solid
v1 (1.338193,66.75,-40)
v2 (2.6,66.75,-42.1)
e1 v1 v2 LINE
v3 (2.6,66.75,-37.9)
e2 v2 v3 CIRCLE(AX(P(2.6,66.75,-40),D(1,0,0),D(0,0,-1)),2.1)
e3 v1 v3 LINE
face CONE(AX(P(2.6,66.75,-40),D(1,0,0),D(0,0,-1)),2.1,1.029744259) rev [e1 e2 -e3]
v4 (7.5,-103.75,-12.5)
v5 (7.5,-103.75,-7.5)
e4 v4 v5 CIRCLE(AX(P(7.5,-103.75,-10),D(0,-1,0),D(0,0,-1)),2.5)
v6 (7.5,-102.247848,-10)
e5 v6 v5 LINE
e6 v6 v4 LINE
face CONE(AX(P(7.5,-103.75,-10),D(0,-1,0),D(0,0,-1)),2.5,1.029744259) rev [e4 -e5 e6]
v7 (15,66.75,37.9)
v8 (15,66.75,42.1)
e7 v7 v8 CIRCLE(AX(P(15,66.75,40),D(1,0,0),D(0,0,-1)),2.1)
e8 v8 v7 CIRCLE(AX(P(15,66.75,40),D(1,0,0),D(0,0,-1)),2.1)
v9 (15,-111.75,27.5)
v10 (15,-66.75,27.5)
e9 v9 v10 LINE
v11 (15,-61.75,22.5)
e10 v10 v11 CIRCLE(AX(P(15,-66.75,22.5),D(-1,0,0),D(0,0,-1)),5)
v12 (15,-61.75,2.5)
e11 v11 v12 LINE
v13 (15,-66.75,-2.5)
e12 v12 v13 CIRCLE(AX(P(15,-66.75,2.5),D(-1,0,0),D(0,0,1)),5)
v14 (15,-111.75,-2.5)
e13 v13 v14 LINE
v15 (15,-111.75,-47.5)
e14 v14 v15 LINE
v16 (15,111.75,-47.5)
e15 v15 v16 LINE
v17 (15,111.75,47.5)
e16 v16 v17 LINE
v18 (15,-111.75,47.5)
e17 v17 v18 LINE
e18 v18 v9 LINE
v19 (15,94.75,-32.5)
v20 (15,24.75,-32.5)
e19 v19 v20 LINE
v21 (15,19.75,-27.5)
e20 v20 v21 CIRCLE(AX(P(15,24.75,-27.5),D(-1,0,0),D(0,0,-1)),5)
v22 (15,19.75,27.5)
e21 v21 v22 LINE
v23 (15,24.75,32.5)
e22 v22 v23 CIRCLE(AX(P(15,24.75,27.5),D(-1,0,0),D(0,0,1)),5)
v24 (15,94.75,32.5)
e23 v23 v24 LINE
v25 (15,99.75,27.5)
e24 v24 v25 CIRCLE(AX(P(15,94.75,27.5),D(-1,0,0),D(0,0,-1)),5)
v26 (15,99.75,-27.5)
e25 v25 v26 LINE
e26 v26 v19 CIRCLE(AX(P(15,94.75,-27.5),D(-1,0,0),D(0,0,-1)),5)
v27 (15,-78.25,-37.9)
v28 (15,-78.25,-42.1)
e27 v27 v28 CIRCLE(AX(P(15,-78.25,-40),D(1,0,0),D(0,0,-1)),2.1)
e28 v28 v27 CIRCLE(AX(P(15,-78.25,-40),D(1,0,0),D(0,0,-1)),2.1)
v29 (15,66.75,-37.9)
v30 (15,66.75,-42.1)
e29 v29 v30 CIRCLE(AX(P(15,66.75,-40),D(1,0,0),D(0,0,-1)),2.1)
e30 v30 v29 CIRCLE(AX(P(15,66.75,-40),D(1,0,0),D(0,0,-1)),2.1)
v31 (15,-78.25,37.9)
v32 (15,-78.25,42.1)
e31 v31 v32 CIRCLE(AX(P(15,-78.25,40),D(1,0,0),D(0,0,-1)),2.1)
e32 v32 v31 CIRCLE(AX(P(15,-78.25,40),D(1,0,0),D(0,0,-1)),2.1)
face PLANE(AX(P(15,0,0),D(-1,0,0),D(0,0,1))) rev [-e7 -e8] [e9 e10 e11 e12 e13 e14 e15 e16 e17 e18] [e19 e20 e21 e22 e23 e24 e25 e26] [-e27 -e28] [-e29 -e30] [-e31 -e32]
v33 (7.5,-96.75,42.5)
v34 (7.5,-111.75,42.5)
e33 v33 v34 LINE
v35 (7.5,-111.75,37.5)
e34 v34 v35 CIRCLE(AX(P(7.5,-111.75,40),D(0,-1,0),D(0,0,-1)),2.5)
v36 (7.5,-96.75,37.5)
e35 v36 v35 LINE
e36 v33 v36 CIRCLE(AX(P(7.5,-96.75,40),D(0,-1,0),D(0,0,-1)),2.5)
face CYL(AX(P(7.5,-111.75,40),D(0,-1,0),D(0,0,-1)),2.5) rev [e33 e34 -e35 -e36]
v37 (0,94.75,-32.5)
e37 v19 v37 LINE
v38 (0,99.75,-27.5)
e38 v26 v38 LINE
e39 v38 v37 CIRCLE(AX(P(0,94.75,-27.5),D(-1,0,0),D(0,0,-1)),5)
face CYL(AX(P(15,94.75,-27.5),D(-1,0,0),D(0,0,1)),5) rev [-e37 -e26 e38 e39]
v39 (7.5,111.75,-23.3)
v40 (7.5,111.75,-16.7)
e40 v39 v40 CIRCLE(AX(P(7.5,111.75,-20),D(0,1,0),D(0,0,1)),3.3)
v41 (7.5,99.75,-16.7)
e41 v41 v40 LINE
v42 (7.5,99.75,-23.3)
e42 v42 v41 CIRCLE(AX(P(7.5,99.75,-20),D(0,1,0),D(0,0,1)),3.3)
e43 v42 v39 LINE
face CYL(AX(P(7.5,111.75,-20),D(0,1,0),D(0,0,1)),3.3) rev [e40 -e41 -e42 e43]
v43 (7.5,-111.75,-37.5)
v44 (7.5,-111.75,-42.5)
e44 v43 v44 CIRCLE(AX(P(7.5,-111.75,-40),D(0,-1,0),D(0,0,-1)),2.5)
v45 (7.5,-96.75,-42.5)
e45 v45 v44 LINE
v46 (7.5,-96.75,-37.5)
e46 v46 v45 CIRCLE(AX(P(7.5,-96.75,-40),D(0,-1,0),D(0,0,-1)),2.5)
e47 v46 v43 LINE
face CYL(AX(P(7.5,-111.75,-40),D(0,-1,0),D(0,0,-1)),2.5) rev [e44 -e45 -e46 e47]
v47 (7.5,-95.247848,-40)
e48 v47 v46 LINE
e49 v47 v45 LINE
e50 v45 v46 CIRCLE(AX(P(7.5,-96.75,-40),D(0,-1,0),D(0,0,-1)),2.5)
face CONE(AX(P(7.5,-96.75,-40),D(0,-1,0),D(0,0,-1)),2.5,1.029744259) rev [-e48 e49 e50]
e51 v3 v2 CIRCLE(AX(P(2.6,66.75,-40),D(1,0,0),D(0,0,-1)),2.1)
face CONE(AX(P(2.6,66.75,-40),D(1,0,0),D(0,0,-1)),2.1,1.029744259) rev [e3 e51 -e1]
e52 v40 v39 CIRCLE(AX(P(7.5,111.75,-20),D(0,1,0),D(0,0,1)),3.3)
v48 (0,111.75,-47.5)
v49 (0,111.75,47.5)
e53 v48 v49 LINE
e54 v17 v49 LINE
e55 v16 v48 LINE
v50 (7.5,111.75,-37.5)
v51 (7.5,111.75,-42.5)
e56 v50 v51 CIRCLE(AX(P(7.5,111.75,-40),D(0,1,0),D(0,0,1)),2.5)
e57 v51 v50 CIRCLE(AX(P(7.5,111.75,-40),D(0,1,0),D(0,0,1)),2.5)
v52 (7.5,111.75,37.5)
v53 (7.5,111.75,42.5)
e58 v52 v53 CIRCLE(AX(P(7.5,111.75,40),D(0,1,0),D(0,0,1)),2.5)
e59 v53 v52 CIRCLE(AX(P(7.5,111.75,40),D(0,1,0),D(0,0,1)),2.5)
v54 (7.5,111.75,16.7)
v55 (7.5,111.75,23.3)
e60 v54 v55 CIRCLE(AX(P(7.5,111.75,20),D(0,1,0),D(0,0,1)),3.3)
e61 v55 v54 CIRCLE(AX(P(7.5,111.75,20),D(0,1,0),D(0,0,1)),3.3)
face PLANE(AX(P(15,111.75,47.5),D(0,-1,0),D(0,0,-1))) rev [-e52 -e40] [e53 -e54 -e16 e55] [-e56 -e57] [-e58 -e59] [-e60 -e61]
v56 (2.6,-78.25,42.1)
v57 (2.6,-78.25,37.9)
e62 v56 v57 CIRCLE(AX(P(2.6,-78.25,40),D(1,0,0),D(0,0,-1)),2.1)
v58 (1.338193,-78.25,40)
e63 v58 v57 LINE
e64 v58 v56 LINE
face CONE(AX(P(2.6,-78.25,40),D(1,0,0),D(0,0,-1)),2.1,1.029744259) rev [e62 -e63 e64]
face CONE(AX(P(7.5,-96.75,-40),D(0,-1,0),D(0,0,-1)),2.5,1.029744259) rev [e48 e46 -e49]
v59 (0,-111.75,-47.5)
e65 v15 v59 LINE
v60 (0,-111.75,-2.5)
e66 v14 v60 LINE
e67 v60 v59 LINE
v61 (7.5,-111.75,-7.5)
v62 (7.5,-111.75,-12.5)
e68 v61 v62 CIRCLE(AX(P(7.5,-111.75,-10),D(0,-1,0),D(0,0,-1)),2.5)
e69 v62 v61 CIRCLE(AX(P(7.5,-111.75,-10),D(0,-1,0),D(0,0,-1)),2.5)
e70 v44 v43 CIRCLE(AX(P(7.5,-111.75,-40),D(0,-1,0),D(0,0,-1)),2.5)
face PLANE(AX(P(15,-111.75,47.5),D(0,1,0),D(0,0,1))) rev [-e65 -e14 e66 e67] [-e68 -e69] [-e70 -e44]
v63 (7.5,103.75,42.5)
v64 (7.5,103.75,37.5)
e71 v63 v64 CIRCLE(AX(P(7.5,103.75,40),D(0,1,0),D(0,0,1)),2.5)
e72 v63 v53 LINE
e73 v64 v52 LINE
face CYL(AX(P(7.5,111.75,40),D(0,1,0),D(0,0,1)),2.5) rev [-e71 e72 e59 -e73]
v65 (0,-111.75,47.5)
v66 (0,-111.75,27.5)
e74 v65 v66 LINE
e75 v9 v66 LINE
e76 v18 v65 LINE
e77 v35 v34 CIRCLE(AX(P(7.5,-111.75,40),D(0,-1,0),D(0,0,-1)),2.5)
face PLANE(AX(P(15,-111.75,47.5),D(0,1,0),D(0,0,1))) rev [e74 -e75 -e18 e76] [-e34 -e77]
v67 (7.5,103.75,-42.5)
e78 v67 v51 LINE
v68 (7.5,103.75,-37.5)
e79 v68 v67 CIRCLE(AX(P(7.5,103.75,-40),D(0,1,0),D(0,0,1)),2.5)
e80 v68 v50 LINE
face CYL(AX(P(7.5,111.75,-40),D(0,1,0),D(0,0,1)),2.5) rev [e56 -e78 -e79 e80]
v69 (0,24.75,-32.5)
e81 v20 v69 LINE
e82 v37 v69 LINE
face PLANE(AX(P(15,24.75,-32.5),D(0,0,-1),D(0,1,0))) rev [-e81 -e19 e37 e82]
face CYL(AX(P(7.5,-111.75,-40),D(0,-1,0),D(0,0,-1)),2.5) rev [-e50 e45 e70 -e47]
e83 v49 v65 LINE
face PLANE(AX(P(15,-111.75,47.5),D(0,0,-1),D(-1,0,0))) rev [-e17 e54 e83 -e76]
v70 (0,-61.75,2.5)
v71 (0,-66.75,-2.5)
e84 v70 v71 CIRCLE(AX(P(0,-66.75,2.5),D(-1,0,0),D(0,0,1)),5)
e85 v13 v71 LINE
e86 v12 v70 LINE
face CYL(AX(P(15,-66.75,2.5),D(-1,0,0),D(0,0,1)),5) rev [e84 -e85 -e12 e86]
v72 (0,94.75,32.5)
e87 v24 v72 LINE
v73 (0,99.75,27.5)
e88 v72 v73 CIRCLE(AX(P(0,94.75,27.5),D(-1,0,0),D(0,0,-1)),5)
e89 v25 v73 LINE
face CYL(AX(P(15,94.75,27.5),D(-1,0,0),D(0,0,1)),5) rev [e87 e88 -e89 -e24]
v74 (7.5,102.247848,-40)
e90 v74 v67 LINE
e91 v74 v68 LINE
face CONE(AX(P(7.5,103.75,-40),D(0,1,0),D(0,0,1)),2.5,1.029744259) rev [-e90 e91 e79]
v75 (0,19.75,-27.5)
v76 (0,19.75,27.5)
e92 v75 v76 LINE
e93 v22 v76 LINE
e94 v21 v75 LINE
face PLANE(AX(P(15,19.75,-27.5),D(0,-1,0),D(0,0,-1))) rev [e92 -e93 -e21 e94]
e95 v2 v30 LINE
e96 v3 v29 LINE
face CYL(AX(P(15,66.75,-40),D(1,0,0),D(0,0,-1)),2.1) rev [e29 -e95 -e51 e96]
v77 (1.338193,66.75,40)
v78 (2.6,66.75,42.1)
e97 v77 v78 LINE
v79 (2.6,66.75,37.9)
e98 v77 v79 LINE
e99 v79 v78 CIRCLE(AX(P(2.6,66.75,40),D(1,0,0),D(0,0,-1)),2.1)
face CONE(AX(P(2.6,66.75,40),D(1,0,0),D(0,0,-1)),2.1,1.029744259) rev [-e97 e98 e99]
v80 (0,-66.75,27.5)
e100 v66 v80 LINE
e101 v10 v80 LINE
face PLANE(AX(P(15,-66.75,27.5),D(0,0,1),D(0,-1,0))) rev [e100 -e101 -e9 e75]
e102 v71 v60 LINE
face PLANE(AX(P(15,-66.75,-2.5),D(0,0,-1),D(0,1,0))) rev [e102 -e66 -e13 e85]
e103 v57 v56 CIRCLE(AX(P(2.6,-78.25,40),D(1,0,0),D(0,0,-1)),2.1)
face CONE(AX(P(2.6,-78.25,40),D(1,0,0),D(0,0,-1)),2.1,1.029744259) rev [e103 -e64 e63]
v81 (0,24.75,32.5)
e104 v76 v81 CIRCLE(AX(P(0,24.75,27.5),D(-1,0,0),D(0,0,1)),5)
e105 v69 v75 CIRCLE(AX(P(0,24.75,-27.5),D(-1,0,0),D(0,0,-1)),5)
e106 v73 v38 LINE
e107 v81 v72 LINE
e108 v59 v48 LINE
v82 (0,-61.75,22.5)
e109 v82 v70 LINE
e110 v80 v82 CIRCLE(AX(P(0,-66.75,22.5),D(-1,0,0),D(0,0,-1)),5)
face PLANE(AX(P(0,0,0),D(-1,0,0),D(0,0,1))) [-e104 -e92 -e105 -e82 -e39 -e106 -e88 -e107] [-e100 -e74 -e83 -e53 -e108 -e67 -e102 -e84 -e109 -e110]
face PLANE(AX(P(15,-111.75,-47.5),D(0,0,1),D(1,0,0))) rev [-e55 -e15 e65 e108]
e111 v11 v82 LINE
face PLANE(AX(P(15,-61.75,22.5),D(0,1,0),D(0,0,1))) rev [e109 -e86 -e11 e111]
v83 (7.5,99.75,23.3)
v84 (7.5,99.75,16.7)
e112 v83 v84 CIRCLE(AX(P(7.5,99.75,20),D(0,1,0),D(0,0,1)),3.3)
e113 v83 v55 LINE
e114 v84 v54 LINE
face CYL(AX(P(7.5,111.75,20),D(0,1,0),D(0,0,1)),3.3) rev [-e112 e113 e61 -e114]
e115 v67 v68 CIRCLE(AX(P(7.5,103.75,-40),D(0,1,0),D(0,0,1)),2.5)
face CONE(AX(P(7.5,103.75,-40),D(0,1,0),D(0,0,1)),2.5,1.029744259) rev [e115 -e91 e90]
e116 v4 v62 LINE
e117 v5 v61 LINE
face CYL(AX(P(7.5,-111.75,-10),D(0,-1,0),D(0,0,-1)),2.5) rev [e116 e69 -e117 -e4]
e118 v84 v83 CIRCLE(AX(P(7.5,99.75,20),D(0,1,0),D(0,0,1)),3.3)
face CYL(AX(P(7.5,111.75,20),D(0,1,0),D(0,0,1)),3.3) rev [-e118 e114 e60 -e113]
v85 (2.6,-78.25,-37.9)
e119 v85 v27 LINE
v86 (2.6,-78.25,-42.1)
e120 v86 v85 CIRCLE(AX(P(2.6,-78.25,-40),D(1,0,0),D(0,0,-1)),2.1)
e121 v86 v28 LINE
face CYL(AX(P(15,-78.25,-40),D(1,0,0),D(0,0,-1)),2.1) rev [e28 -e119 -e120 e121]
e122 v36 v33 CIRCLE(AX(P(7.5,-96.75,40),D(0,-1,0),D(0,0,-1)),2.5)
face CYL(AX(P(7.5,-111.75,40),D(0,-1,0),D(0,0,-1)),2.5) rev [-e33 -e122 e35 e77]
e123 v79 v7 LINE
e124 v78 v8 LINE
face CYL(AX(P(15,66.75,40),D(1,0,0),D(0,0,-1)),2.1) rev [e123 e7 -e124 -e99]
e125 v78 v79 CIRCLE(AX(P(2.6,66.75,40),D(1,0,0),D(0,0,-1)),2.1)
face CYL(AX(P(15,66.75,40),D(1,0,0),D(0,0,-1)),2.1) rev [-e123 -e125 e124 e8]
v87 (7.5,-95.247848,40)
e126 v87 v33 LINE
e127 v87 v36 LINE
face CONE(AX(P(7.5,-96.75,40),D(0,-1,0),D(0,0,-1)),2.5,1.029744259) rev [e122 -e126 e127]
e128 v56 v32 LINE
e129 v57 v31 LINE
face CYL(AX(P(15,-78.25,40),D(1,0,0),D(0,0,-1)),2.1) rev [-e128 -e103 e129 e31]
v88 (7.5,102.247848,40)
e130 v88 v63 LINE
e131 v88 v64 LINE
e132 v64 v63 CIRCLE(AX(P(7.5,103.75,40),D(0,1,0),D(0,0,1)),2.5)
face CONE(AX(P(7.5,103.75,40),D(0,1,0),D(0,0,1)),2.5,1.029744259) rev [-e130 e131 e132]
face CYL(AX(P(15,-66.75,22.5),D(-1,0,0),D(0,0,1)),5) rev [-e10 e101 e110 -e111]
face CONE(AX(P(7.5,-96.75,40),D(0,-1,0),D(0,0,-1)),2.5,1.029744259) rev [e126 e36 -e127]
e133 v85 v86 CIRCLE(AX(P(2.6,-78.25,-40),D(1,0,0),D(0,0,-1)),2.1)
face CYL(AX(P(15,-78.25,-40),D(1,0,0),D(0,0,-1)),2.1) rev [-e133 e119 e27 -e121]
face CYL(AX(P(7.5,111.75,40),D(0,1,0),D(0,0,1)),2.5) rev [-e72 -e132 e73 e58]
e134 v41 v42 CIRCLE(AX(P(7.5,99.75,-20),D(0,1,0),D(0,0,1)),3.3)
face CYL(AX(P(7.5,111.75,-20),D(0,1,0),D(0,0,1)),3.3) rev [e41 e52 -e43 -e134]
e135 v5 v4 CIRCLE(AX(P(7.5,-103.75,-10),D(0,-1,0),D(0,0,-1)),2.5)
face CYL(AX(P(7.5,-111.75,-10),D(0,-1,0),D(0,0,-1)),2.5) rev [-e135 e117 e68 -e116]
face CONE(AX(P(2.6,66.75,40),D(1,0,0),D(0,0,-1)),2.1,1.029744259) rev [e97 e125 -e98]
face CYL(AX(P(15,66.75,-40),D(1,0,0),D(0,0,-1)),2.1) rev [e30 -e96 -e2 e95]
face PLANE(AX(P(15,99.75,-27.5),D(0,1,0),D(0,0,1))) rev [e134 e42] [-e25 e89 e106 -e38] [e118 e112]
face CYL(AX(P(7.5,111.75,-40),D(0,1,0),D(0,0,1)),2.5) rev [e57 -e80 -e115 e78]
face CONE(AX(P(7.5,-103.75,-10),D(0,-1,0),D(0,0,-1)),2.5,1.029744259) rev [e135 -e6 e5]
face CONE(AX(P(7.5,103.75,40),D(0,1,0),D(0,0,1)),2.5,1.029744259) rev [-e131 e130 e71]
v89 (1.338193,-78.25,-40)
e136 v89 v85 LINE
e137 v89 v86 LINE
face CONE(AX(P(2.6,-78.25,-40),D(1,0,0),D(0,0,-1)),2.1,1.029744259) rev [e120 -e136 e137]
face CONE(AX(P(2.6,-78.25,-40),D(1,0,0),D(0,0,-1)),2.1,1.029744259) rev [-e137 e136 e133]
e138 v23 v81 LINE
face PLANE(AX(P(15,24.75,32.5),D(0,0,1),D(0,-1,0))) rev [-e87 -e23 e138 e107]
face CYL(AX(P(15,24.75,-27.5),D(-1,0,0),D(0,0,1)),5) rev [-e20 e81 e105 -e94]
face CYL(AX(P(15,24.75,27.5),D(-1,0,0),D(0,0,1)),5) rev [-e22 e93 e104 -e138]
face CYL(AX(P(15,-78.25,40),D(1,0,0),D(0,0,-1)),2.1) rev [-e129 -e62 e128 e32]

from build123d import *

# Parameters (mm, degrees)
SKETCH1_W                  = 95
SKETCH1_H                  = 223.5
BOSS_EXTRUDE1_DEPTH        = 15
CUT_EXTRUDE1_DEPTH         = 123.349141803
M6_CLEARANCE_HOLE1_D       = 6.6
M6_CLEARANCE_HOLE1_DEPTH   = 19.75
M6_CLEARANCE_HOLE1_TIP     = 1.982840043
M6_TAPPED_HOLE1_D          = 5
M6_TAPPED_HOLE1_DEPTH      = 15
M6_TAPPED_HOLE1_TIP        = 1.502151548
F_5_0MM_BLIND_HOLE_1_D     = 5
F_5_0MM_BLIND_HOLE_1_DEPTH = 8
F_5_0MM_BLIND_HOLE_1_TIP   = 1.502151548
F_5_0MM_BLIND_HOLE_2_D     = 5
F_5_0MM_BLIND_HOLE_2_DEPTH = 8
F_5_0MM_BLIND_HOLE_2_TIP   = 1.502151548
M5_TAPPED_HOLE1_D          = 4.2
M5_TAPPED_HOLE1_DEPTH      = 12.4
M5_TAPPED_HOLE1_TIP        = 1.2618073


with BuildPart() as part:
    # Sketch1 → Boss-Extrude1 (new body)
    with BuildSketch(Plane(origin=(0, 0, 0), x_dir=(0, 0, -1), z_dir=(1, 0, 0))):
        Rectangle(SKETCH1_W, SKETCH1_H)
    extrude(amount=BOSS_EXTRUDE1_DEPTH)

    # Sketch2 → Cut-Extrude1 (cut, through all)
    with BuildSketch(Plane.ZY):
        with BuildLine():
            Line((22.5, -61.75), (2.5, -61.75))
            ThreePointArc((2.5, -61.75), (-1.035533906, -63.214466094), (-2.5, -66.75))
            Line((-2.5, -66.75), (-2.5, -111.75))
            Line((-2.5, -111.75), (27.5, -111.75))
            Line((27.5, -111.75), (27.5, -66.75))
            ThreePointArc((27.5, -66.75), (26.035533906, -63.214466094), (22.5, -61.75))
        make_face()
        with BuildLine():
            Line((-27.5, 19.75), (27.5, 19.75))
            ThreePointArc((27.5, 19.75), (31.035533906, 21.214466094), (32.5, 24.75))
            Line((32.5, 24.75), (32.5, 94.75))
            ThreePointArc((32.5, 94.75), (31.035533906, 98.285533906), (27.5, 99.75))
            Line((27.5, 99.75), (-27.5, 99.75))
            ThreePointArc((-27.5, 99.75), (-31.035533906, 98.285533906), (-32.5, 94.75))
            Line((-32.5, 94.75), (-32.5, 24.75))
            ThreePointArc((-32.5, 24.75), (-31.035533906, 21.214466094), (-27.5, 19.75))
        make_face()
    extrude(amount=-CUT_EXTRUDE1_DEPTH, mode=Mode.SUBTRACT)

    # M6 Clearance Hole1
    with Locations(Plane(origin=(0, 111.75, 0), x_dir=(1, 0, 0), z_dir=(0, 1, 0))):
        with Locations((7.5, -20), (7.5, 20)):
            Hole(M6_CLEARANCE_HOLE1_D / 2, depth=M6_CLEARANCE_HOLE1_DEPTH)
            with Locations((0, 0, -(M6_CLEARANCE_HOLE1_DEPTH + M6_CLEARANCE_HOLE1_TIP / 2))):  # 118° drill point
                Cone(0, M6_CLEARANCE_HOLE1_D / 2, M6_CLEARANCE_HOLE1_TIP, mode=Mode.SUBTRACT)

    # M6 Tapped Hole1
    with Locations(Plane(origin=(0, -111.75, 0), x_dir=(-1, 0, 0), z_dir=(0, -1, 0))):
        with Locations((-7.5, -40), (-7.5, 40)):
            Hole(M6_TAPPED_HOLE1_D / 2, depth=M6_TAPPED_HOLE1_DEPTH)
            with Locations((0, 0, -(M6_TAPPED_HOLE1_DEPTH + M6_TAPPED_HOLE1_TIP / 2))):  # 118° drill point
                Cone(0, M6_TAPPED_HOLE1_D / 2, M6_TAPPED_HOLE1_TIP, mode=Mode.SUBTRACT)

    # Ø5.0mm blind hole 1
    with Locations(Plane(origin=(0, -111.75, 0), x_dir=(-1, 0, 0), z_dir=(0, -1, 0))):
        with Locations((-7.5, 10)):
            Hole(F_5_0MM_BLIND_HOLE_1_D / 2, depth=F_5_0MM_BLIND_HOLE_1_DEPTH)
            with Locations((0, 0, -(F_5_0MM_BLIND_HOLE_1_DEPTH + F_5_0MM_BLIND_HOLE_1_TIP / 2))):  # 118° drill point
                Cone(0, F_5_0MM_BLIND_HOLE_1_D / 2, F_5_0MM_BLIND_HOLE_1_TIP, mode=Mode.SUBTRACT)

    # Ø5.0mm blind hole 2
    with Locations(Plane(origin=(0, 111.75, 0), x_dir=(1, 0, 0), z_dir=(0, 1, 0))):
        with Locations((7.5, -40), (7.5, 40)):
            Hole(F_5_0MM_BLIND_HOLE_2_D / 2, depth=F_5_0MM_BLIND_HOLE_2_DEPTH)
            with Locations((0, 0, -(F_5_0MM_BLIND_HOLE_2_DEPTH + F_5_0MM_BLIND_HOLE_2_TIP / 2))):  # 118° drill point
                Cone(0, F_5_0MM_BLIND_HOLE_2_D / 2, F_5_0MM_BLIND_HOLE_2_TIP, mode=Mode.SUBTRACT)

    # M5 Tapped Hole1
    with Locations(Plane(origin=(15, 0, 0), x_dir=(0, 0, -1), z_dir=(1, 0, 0))):
        with Locations((40, 66.75), (-40, 66.75), (40, -78.25), (-40, -78.25)):
            Hole(M5_TAPPED_HOLE1_D / 2, depth=M5_TAPPED_HOLE1_DEPTH)
            with Locations((0, 0, -(M5_TAPPED_HOLE1_DEPTH + M5_TAPPED_HOLE1_TIP / 2))):  # 118° drill point
                Cone(0, M5_TAPPED_HOLE1_D / 2, M5_TAPPED_HOLE1_TIP, mode=Mode.SUBTRACT)


solid = part.part
